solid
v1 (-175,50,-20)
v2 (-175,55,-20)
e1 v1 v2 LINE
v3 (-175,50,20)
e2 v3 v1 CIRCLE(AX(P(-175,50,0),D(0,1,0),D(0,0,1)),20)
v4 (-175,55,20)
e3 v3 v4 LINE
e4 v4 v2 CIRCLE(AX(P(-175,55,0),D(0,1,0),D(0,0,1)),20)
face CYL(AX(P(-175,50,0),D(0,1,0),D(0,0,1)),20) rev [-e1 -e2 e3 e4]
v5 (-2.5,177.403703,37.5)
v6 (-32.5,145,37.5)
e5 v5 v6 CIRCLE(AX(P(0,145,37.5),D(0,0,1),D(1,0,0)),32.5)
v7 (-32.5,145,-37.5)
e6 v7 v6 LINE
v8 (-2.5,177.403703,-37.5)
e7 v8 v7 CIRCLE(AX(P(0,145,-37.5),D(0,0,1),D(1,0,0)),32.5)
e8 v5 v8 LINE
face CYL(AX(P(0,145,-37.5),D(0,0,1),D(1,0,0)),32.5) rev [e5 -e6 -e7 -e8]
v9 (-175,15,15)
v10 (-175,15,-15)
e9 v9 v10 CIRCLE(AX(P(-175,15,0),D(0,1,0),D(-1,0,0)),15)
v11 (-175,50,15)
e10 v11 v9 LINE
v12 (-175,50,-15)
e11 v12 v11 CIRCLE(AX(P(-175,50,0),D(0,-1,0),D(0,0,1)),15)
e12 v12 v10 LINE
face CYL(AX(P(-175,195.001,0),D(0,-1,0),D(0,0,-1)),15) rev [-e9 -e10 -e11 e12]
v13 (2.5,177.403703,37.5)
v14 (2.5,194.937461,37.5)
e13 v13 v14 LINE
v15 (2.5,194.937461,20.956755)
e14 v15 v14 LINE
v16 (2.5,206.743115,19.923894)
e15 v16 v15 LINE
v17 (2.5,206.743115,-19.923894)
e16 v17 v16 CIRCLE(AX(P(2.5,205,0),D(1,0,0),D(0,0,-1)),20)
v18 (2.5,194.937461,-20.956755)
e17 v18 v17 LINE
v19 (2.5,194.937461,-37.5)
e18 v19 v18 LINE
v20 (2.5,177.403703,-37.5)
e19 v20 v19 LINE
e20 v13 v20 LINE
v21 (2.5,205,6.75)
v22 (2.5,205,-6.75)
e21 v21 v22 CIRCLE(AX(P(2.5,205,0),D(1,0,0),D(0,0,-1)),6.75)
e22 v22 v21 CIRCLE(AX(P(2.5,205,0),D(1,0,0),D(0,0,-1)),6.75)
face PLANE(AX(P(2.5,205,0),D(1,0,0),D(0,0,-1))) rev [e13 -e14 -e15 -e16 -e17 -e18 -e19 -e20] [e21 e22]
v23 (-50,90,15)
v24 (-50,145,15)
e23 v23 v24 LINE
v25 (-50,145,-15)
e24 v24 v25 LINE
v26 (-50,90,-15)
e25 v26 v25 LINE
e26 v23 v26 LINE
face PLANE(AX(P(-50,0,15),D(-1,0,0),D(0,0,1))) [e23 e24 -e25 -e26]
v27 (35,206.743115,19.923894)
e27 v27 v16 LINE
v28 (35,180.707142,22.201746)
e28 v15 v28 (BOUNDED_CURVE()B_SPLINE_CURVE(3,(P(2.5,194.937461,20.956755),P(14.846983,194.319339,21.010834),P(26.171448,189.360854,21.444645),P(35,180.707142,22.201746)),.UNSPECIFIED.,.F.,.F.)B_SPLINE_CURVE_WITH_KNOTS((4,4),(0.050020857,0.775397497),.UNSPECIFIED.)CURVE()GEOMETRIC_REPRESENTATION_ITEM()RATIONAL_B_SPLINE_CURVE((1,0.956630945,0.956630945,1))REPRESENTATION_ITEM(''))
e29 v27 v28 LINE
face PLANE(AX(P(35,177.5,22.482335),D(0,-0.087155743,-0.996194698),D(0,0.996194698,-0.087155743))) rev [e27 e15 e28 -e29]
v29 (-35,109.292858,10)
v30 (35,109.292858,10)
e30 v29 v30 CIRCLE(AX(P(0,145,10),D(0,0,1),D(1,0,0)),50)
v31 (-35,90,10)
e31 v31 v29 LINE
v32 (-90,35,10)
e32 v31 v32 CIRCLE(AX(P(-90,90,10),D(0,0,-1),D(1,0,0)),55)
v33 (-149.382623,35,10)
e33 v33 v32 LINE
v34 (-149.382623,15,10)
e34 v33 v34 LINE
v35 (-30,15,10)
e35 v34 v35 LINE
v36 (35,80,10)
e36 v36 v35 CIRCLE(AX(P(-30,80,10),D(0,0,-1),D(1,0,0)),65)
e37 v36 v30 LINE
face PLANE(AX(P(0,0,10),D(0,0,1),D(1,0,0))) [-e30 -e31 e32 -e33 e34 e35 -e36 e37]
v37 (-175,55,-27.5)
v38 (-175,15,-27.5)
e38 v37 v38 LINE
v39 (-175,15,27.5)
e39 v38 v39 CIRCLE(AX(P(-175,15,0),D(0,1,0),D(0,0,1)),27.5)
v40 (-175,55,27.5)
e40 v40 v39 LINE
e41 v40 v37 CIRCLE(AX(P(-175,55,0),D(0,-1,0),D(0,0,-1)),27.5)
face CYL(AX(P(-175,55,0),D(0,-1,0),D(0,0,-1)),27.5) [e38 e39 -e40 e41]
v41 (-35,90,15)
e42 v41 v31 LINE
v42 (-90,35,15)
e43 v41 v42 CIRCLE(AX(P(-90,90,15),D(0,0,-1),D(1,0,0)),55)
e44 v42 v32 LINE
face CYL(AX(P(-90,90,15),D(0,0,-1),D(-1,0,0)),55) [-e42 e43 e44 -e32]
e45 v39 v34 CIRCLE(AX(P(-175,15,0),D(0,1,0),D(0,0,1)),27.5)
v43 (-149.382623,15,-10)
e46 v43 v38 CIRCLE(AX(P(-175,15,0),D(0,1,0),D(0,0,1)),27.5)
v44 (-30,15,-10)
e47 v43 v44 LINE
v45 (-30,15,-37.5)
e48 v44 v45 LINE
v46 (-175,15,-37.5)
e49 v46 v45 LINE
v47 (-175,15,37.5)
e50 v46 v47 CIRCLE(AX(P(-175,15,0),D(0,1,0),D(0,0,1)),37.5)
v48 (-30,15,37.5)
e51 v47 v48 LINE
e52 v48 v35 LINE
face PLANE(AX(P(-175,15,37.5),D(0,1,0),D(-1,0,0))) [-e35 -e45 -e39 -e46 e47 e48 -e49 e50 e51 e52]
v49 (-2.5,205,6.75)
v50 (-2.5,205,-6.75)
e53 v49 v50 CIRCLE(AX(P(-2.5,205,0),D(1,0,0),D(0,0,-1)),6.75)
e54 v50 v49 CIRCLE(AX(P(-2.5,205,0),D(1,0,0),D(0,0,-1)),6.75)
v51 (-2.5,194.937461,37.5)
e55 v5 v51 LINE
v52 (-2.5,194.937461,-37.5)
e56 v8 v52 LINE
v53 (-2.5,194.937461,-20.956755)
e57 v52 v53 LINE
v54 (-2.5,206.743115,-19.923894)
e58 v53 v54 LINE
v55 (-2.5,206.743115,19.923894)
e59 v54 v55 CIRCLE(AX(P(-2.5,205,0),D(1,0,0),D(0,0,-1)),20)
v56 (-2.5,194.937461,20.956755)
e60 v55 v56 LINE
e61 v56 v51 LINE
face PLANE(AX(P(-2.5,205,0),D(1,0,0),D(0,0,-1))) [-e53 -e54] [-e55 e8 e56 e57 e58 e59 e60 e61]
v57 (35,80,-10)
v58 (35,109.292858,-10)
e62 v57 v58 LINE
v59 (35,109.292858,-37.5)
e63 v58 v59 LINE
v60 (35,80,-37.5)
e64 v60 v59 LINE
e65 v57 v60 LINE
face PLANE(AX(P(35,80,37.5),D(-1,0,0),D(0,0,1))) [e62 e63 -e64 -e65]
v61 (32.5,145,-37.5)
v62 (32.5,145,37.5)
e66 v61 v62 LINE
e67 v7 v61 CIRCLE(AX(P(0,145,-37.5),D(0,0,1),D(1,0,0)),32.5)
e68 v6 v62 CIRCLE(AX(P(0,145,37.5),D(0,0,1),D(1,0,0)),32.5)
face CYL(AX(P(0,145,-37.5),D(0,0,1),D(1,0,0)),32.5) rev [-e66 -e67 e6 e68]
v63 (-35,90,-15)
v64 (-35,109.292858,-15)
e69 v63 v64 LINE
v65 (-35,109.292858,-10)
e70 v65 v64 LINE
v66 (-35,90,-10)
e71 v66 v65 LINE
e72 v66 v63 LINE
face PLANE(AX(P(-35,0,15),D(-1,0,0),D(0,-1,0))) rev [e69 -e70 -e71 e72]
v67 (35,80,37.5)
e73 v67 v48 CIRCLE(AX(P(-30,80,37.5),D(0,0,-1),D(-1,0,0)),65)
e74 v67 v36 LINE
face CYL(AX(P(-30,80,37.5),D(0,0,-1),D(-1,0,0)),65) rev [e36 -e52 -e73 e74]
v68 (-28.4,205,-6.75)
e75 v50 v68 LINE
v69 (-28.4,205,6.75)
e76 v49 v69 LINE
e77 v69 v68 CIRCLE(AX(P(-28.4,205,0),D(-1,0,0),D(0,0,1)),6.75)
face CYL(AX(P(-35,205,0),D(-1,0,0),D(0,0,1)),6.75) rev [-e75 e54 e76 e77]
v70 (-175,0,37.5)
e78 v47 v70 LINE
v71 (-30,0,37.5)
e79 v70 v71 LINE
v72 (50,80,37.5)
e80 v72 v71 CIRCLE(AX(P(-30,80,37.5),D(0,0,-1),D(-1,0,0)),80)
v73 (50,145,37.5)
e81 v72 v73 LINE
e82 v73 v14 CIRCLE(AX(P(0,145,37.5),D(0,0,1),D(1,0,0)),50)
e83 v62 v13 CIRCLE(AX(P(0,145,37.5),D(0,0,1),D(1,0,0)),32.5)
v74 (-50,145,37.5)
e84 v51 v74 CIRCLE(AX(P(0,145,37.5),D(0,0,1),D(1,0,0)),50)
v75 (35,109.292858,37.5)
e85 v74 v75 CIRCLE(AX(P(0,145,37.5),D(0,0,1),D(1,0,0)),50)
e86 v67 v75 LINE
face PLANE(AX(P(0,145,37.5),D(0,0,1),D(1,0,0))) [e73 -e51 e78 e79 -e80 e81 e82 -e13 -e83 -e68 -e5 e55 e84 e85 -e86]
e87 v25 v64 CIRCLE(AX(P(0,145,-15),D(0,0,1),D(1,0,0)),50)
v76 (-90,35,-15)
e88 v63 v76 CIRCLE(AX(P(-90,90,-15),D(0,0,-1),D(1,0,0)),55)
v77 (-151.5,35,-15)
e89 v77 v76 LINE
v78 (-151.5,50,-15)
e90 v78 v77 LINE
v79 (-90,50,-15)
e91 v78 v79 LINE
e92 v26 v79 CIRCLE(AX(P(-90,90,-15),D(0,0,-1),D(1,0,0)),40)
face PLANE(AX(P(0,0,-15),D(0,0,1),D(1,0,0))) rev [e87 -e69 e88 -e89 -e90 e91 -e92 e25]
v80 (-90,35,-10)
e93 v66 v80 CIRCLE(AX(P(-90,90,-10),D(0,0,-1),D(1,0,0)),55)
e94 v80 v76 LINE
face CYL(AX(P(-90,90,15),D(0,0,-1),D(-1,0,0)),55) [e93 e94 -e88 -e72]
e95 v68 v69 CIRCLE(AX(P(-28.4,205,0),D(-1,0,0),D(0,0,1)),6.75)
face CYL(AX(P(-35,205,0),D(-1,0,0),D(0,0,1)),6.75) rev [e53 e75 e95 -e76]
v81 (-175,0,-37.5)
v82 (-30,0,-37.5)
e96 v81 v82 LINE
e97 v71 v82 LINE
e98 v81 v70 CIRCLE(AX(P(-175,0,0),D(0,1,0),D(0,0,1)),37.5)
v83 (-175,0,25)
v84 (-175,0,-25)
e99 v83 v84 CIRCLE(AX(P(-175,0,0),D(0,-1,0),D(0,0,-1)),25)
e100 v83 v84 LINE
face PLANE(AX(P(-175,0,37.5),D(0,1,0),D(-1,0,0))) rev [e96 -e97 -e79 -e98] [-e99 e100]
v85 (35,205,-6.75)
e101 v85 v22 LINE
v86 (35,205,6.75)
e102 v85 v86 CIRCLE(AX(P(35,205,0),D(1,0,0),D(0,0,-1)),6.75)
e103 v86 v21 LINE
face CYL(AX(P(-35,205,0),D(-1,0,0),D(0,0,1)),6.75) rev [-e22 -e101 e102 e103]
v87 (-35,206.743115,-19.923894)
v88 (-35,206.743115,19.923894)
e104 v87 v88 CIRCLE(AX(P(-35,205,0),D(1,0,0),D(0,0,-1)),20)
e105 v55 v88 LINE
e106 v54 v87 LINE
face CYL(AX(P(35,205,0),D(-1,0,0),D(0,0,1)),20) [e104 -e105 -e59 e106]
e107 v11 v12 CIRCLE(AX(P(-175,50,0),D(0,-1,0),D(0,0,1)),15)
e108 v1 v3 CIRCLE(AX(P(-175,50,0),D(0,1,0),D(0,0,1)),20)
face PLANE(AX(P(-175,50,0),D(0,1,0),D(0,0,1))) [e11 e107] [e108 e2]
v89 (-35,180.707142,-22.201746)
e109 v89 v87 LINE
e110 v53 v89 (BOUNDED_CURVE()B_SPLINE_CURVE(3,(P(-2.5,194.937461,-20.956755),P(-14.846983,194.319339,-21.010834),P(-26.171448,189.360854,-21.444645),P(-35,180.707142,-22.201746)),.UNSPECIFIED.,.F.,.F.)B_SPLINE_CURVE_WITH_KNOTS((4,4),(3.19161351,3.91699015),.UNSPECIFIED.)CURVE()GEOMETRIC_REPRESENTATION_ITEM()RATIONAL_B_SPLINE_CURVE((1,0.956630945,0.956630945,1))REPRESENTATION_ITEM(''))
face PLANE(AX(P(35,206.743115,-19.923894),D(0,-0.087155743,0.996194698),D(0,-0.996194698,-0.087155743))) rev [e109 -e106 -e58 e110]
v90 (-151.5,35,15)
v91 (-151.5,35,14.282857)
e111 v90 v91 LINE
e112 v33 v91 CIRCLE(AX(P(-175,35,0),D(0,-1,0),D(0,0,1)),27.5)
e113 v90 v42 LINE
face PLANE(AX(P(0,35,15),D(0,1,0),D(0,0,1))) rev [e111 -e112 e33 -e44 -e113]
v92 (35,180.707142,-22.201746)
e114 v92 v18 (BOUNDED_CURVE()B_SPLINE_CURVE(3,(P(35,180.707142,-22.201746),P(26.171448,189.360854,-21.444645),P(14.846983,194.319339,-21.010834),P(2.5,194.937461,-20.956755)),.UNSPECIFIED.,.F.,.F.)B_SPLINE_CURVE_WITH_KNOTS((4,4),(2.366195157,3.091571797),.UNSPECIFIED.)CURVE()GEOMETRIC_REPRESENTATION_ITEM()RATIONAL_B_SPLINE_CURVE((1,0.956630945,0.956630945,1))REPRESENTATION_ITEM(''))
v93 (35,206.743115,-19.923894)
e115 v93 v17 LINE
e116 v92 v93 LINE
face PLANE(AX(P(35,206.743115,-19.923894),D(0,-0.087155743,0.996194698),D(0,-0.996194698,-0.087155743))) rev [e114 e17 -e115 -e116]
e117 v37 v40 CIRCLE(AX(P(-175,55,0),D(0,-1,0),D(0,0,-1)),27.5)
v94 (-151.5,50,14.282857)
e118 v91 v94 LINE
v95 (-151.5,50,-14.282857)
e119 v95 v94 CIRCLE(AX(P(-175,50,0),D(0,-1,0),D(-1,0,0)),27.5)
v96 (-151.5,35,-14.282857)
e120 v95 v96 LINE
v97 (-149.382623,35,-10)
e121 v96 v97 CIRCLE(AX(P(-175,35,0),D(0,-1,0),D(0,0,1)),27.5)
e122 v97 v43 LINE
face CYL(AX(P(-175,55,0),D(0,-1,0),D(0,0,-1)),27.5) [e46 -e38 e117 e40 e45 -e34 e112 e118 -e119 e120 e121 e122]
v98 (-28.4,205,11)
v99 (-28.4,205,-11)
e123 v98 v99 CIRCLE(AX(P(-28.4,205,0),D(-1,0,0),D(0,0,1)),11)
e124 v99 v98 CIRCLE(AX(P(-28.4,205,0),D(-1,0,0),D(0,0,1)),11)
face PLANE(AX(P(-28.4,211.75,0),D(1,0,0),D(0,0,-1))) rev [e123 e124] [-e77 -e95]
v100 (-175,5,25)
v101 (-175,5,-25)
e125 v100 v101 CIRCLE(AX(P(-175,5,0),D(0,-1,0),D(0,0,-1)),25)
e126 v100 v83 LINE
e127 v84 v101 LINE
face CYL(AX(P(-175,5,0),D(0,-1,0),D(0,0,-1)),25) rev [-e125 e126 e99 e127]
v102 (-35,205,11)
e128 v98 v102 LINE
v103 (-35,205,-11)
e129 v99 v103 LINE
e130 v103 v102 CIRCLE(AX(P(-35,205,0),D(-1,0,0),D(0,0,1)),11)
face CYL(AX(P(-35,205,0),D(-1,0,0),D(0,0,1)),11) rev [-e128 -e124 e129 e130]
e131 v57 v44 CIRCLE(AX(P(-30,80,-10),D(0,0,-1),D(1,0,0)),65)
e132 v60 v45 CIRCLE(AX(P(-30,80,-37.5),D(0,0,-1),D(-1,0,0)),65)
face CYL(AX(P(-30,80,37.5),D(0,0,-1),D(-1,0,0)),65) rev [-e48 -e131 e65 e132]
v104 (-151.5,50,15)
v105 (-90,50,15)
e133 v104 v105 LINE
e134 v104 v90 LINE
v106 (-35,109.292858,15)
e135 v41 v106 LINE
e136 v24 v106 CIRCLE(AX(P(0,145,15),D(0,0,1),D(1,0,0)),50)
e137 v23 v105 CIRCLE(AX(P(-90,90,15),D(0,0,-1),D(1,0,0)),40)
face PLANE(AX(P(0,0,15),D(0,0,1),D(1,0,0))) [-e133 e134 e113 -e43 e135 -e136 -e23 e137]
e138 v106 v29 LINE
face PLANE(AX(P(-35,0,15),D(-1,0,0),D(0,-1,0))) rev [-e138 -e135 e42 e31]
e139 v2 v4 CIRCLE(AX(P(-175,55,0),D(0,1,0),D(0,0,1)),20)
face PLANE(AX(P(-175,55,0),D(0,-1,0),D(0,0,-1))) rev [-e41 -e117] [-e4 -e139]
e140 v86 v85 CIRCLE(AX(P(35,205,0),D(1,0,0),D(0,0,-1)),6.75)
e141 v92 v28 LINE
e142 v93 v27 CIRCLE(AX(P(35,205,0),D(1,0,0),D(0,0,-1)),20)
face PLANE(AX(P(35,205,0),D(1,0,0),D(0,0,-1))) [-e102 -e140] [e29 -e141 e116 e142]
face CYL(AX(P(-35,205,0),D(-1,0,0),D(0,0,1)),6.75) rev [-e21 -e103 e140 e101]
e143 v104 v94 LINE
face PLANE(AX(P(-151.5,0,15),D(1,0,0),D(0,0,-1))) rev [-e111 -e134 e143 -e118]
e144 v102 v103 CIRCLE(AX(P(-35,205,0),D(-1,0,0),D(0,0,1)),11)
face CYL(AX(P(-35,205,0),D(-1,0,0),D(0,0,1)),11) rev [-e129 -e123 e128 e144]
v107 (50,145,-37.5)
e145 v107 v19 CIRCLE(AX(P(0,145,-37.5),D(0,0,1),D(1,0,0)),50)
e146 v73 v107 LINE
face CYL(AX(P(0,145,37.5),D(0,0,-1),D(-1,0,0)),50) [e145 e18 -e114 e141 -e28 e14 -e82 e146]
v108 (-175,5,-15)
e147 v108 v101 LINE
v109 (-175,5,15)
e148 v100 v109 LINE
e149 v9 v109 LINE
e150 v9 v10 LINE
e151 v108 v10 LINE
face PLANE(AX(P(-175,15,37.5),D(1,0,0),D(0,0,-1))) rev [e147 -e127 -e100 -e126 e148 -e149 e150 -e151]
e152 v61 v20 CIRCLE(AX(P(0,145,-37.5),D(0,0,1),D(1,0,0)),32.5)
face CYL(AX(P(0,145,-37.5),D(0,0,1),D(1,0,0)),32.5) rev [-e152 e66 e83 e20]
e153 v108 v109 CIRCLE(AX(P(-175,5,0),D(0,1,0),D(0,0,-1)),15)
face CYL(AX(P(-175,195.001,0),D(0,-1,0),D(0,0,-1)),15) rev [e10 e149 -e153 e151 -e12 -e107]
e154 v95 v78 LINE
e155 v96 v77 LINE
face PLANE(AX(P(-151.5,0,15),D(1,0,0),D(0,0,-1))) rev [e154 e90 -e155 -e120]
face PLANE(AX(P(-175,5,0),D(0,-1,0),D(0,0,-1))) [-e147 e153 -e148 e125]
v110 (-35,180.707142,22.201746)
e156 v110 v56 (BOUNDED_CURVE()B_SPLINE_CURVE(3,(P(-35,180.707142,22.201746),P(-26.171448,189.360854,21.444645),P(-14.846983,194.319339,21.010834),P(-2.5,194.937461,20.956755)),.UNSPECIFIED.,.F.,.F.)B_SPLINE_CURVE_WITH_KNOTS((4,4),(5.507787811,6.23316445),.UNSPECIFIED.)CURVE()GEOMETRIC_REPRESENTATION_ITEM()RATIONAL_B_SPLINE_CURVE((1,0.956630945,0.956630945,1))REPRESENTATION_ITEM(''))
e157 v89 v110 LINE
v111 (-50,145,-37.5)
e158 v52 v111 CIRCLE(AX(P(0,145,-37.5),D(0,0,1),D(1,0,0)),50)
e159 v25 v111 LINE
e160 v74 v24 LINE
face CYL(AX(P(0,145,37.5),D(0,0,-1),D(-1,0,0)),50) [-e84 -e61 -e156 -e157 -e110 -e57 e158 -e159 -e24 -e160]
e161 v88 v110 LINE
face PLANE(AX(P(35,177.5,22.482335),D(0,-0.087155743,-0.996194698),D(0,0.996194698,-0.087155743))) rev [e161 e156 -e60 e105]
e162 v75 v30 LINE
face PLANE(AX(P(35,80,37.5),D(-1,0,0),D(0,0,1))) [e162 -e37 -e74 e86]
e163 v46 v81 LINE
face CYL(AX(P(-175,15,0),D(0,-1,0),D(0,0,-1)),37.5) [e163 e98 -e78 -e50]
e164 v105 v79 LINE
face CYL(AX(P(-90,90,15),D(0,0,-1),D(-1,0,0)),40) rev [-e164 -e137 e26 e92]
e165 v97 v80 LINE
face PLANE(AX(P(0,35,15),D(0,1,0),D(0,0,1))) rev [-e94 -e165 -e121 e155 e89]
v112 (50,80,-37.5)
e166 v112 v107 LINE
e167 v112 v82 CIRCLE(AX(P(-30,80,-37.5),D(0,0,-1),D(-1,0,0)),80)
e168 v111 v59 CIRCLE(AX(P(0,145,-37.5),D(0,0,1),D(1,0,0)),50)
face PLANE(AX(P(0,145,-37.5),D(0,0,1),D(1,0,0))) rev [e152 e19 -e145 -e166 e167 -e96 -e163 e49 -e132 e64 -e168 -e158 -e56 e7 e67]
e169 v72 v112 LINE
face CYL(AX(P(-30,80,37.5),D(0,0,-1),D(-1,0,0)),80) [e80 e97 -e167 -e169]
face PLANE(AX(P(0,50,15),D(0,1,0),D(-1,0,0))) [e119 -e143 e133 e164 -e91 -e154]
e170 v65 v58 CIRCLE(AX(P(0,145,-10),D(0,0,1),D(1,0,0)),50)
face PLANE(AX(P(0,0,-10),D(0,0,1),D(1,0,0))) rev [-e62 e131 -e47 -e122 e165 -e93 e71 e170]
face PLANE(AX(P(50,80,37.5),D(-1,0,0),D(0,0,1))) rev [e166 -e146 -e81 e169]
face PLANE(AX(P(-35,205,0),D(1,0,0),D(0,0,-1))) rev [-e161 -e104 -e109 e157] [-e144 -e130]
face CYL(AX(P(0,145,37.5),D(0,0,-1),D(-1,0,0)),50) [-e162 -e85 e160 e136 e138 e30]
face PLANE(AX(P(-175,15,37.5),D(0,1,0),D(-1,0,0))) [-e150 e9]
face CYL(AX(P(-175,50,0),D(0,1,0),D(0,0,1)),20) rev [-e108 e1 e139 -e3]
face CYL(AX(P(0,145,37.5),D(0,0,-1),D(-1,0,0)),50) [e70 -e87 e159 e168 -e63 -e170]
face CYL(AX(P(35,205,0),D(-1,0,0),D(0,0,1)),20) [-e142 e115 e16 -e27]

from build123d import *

# Parameters (mm, degrees)
MOUNT_SIDE_PROFILE_SKETCH_R            = 50
MOUNT_SIDE_PROFILE_SKETCH_R_2          = 32.5
CLAMP_COLLAR_BODY_DEPTH                = 37.5
BASE_PLATE_SKETCH_R                    = 37.5
BASE_PLATE_15MM_DEPTH                  = 15
SOCKET_BOSS_SKETCH_R                   = 27.5
SOCKET_BOSS_DEPTH                      = 55
SKETCH10_3_R                           = 25
SOCKET_BOSS_RELIEF_CUT_DEPTH           = 5
SOCKET_START                           = -55
SKETCH10_4_R                           = 15
SOCKET_BORE_DEPTH                      = 50
SOCKET_COUNTERBORE_SKETCH_40_R         = 20
SOCKET_COUNTERBORE_40_DEPTH            = 5
CURVED_ARM_DEPTH                       = 37.5
PIPE_BORE_CUT_DEPTH                    = 291.839302709
PIPE_BORE_CUT_DEPTH_BACK               = 291.839302709
SKETCH1_2_R                            = 32.5
ARM_RIB_20MM_DEPTH                     = 10
ARM_WEB_30MM_DEPTH                     = 15
CLAMP_LUG_DEPTH                        = 35
CLAMP_SPLIT_SLOT_DEPTH                 = 2.5
CLAMP_BOLT_HOLE_CBORE_13_5_D           = 13.5
CLAMP_BOLT_HOLE_CBORE_13_5_CBORE_D     = 22
CLAMP_BOLT_HOLE_CBORE_13_5_CBORE_DEPTH = 6.6


with BuildPart() as part:
    # Mount Side Profile Sketch → Clamp Collar Body (new, symmetric)
    with BuildSketch(Plane.XY):
        with Locations((0, 145)):
            Circle(MOUNT_SIDE_PROFILE_SKETCH_R)
        with Locations((0, 145)):
            Circle(MOUNT_SIDE_PROFILE_SKETCH_R_2, mode=Mode.SUBTRACT)
    extrude(amount=CLAMP_COLLAR_BODY_DEPTH, both=True)



with BuildPart() as body_2:
    # Base Plate Sketch → Base Plate 15mm (new body)
    with BuildSketch(Plane(origin=(0, 0, 0), x_dir=(1, 0, 0), z_dir=(0, 1, 0))):
        with Locations(Location((-175, 0, 0), (0, 0, 270))):
            Circle(BASE_PLATE_SKETCH_R)
    extrude(amount=BASE_PLATE_15MM_DEPTH)

    # Socket Boss Sketch → Socket Boss (add)
    with BuildSketch(Plane.XZ):
        with Locations(Location((-175, 0, 0), (0, 0, 270))):
            Circle(SOCKET_BOSS_SKETCH_R)
    extrude(amount=-SOCKET_BOSS_DEPTH)

    # Sketch10_3 → Socket Boss Relief Cut (cut)
    with BuildSketch(Plane.XZ):
        with Locations(Location((-175, 0, 0), (0, 0, 270))):
            Circle(SKETCH10_3_R)
    extrude(amount=-SOCKET_BOSS_RELIEF_CUT_DEPTH, mode=Mode.SUBTRACT)

    # Sketch10_4 → Socket Bore (cut)
    with BuildSketch(Plane.XZ.offset(SOCKET_START)):
        with Locations(Location((-175, 0, 0), (0, 0, 270))):
            Circle(SKETCH10_4_R)
    extrude(amount=SOCKET_BORE_DEPTH, mode=Mode.SUBTRACT)

    # Socket Counterbore Sketch _40 → Socket Counterbore _40 (cut)
    with BuildSketch(Plane(origin=(0, 55, 0), x_dir=(1, 0, 0), z_dir=(0, 1, 0))):
        with Locations(Location((-175, 0, 0), (0, 0, 270))):
            Circle(SOCKET_COUNTERBORE_SKETCH_40_R)
    extrude(amount=-SOCKET_COUNTERBORE_40_DEPTH, mode=Mode.SUBTRACT)


with BuildPart() as part_1:
    add(part.part)

    add(body_2.part)  # Curved Arm merges body 2
    # Curved Arm Profile Sketch → Curved Arm (add, symmetric)
    with BuildSketch(Plane.XY):
        with BuildLine():
            Line((-175, 0), (-30, 0))
            ThreePointArc((-30, 0), (26.568542495, 23.431457505), (50, 80))
            Line((50, 80), (50, 145))
            ThreePointArc((50, 145), (-46.097722286, 164.364916731), (35, 109.292857857))
            Line((35, 109.292857857), (35, 80))
            ThreePointArc((35, 80), (15.961940777, 34.038059223), (-30, 15))
            Line((-30, 15), (-175, 15))
            Line((-175, 15), (-175, 0))
        make_face()
    extrude(amount=CURVED_ARM_DEPTH, both=True)

    # Sketch1_2 → Pipe Bore Cut (cut, two sides: drawn at the far end of the back side and taken through both)
    with BuildSketch(Plane.XY.offset(-PIPE_BORE_CUT_DEPTH_BACK)):
        with Locations((0, 145)):
            Circle(SKETCH1_2_R)
    extrude(amount=PIPE_BORE_CUT_DEPTH + PIPE_BORE_CUT_DEPTH_BACK, mode=Mode.SUBTRACT)

    # Sketch12_3 → Arm Rib 20mm (add, symmetric)
    with BuildSketch(Plane.XY):
        with BuildLine():
            Line((-151.5, 35), (-151.5, 15))
            Line((-151.5, 15), (-30, 15))
            ThreePointArc((-30, 15), (15.961940777, 34.038059223), (35, 80))
            Line((35, 80), (35, 109.292857857))
            ThreePointArc((35, 109.292857857), (0, 95), (-35, 109.292857857))
            Line((-35, 109.292857857), (-35, 90))
            ThreePointArc((-35, 90), (-51.109127035, 51.109127035), (-90, 35))
            Line((-90, 35), (-151.5, 35))
        make_face()
    extrude(amount=ARM_RIB_20MM_DEPTH, both=True)

    # Sketch12_4 → Arm Web 30mm (add, symmetric)
    with BuildSketch(Plane.XY):
        with BuildLine():
            Line((-151.5, 50), (-151.5, 35))
            Line((-151.5, 35), (-90, 35))
            ThreePointArc((-90, 35), (-51.109127035, 51.109127035), (-35, 90))
            Line((-35, 90), (-35, 109.292857857))
            ThreePointArc((-35, 109.292857857), (-46.097722286, 125.635083269), (-50, 145))
            Line((-50, 145), (-50, 90))
            ThreePointArc((-50, 90), (-61.715728753, 61.715728753), (-90, 50))
            Line((-90, 50), (-151.5, 50))
        make_face()
    extrude(amount=ARM_WEB_30MM_DEPTH, both=True)

    # Clamp Lug Sketch → Clamp Lug (add, symmetric)
    with BuildSketch(Plane(origin=(0, 0, 0), x_dir=(0, 0, -1), z_dir=(1, 0, 0))):
        with BuildLine():
            Line((19.923893962, 206.743114855), (22.482334998, 177.5))
            Line((22.482334998, 177.5), (-22.482334998, 177.5))
            Line((-22.482334998, 177.5), (-19.923893962, 206.743114855))
            ThreePointArc((-19.923893962, 206.743114855), (0, 225), (19.923893962, 206.743114855))
        make_face()
    extrude(amount=CLAMP_LUG_DEPTH, both=True)

    # Clamp Split Slot Sketch → Clamp Split Slot (cut, symmetric)
    with BuildSketch(Plane(origin=(0, 0, 0), x_dir=(0, 0, -1), z_dir=(1, 0, 0))):
        with BuildLine():
            Line((-37.855398527, 208.311918224), (-41.845299437, 162.707142143))
            Line((-41.845299437, 162.707142143), (41.845299437, 162.707142143))
            Line((41.845299437, 162.707142143), (37.855398527, 208.311918224))
            ThreePointArc((37.855398527, 208.311918224), (0, 243), (-37.855398527, 208.311918224))
        make_face()
    extrude(amount=CLAMP_SPLIT_SLOT_DEPTH, both=True, mode=Mode.SUBTRACT)

    # Clamp Bolt Hole CBore _13.5 (through all)
    with Locations(Plane.ZY.offset(35)):
        with Locations((0, 205)):
            CounterBoreHole(CLAMP_BOLT_HOLE_CBORE_13_5_D / 2, CLAMP_BOLT_HOLE_CBORE_13_5_CBORE_D / 2, CLAMP_BOLT_HOLE_CBORE_13_5_CBORE_DEPTH)


solid = part_1.part
